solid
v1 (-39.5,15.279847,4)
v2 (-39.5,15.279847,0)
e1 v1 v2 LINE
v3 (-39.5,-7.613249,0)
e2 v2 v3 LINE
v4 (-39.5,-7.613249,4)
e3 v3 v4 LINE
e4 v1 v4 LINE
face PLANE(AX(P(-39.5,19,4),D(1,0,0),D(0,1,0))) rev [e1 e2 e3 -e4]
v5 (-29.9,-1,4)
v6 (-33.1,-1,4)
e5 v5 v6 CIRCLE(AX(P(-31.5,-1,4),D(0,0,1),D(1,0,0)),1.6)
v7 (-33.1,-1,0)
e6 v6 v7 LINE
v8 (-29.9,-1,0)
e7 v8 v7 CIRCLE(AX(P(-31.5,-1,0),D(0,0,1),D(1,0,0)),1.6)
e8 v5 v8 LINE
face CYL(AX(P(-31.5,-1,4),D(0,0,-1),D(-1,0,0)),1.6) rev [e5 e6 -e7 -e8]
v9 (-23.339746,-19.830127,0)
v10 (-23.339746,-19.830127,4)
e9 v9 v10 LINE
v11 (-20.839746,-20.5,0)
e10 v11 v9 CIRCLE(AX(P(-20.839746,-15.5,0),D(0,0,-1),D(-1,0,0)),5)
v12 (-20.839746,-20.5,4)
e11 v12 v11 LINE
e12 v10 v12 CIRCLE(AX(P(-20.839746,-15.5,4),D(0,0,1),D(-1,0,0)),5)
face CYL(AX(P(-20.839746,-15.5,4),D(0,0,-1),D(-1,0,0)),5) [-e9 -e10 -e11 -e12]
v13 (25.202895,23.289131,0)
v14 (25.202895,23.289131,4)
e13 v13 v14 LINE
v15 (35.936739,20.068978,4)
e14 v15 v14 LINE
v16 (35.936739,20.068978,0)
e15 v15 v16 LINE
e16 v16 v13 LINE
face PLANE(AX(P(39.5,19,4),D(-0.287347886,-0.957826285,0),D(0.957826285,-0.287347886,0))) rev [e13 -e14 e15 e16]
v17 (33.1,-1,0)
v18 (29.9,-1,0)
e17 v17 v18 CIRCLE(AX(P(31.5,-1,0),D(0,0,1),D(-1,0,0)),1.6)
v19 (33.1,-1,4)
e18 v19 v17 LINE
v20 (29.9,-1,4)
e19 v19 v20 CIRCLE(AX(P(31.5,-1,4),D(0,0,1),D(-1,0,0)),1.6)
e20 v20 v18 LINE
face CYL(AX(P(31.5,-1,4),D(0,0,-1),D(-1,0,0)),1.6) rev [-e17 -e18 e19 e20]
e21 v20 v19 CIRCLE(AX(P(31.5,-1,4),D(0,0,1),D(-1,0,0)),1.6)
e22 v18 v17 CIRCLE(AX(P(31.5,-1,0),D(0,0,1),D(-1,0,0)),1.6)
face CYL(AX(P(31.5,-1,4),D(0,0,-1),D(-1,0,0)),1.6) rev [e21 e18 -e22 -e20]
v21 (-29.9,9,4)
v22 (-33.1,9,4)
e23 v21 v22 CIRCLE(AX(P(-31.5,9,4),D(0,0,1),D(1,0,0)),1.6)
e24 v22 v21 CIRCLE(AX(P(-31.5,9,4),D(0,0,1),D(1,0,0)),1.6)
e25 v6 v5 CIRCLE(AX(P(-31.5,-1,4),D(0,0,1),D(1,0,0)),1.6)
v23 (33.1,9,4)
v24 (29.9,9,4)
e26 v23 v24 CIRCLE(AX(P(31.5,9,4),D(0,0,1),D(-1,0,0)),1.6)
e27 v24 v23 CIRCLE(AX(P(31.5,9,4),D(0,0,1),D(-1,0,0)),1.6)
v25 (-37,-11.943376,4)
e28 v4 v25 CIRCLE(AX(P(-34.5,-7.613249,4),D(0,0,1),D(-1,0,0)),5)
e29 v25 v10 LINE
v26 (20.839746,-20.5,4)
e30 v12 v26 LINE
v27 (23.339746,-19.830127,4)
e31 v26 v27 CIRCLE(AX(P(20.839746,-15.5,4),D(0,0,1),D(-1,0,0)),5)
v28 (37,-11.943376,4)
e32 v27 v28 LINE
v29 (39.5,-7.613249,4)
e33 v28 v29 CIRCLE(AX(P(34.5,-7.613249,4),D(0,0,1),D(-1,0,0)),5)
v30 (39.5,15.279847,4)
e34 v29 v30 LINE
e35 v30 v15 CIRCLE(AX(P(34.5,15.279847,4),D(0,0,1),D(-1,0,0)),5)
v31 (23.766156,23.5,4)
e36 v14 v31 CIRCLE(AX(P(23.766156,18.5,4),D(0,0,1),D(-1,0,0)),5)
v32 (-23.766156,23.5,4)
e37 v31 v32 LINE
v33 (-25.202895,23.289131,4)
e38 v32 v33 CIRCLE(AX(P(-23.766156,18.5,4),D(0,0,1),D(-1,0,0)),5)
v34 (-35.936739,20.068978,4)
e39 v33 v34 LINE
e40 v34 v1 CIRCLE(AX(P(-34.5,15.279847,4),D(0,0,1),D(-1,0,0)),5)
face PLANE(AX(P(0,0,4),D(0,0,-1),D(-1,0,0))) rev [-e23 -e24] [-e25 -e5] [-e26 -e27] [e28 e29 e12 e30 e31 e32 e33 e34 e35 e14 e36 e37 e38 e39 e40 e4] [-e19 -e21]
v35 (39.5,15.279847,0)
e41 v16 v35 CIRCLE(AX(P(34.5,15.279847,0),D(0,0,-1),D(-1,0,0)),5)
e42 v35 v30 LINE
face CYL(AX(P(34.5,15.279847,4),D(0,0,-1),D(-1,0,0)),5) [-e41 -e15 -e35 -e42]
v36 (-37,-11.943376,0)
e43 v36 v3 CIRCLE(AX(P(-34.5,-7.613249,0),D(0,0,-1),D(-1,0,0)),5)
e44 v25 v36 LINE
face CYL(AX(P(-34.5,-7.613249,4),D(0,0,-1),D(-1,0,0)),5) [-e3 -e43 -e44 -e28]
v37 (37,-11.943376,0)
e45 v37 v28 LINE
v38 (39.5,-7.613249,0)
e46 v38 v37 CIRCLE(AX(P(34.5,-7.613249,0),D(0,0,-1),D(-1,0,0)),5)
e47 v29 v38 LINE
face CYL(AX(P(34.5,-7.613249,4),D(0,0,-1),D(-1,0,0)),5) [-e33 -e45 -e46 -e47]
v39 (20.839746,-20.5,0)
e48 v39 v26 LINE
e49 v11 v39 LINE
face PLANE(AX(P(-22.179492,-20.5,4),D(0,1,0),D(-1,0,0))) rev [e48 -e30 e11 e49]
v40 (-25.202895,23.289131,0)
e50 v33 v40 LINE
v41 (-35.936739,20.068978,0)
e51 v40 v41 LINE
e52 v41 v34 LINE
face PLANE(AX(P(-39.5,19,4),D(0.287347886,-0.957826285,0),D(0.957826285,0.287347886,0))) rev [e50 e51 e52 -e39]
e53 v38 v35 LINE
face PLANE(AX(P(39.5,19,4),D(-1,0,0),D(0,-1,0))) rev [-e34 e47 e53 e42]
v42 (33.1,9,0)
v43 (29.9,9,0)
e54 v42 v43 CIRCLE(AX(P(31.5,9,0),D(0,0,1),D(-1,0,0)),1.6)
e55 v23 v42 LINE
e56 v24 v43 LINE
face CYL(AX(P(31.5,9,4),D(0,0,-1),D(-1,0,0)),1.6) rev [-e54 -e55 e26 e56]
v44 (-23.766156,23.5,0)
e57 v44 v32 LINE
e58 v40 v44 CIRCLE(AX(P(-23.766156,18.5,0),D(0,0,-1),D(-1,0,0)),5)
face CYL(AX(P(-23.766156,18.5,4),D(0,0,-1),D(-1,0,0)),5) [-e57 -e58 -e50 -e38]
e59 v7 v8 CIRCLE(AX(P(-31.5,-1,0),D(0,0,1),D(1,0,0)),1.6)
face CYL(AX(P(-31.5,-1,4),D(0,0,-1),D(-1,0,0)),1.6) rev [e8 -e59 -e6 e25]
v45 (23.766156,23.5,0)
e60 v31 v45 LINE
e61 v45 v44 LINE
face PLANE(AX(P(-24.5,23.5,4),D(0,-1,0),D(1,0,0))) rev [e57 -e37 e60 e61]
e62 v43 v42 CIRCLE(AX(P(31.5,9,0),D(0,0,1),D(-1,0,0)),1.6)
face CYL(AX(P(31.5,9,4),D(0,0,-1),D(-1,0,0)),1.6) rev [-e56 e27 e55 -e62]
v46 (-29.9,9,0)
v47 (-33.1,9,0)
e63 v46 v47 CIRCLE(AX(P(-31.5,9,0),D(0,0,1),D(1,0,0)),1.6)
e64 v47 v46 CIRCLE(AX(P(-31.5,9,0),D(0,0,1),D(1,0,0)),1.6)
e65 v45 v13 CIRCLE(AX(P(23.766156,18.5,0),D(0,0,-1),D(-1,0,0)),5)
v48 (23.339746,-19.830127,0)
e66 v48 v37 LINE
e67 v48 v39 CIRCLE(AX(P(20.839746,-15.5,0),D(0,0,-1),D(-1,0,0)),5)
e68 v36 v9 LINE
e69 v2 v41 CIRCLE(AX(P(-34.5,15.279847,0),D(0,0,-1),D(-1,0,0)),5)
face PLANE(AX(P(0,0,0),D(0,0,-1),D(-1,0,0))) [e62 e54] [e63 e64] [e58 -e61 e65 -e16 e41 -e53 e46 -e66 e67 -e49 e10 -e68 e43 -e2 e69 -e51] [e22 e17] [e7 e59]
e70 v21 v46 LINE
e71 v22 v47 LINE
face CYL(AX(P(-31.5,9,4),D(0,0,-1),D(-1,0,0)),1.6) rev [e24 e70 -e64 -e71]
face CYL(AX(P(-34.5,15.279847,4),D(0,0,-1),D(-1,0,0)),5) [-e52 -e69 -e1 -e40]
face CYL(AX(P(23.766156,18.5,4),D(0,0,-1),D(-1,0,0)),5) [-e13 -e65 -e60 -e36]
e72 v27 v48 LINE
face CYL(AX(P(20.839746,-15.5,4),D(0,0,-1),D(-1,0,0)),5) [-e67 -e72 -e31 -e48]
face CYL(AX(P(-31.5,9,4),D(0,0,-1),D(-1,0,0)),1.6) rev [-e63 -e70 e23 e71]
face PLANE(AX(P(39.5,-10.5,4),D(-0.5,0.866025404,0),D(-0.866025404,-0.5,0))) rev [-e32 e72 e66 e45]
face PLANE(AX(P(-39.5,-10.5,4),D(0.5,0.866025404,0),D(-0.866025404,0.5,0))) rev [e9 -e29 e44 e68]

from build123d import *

# Parameters (mm, degrees)
SKETCH_1_R      = 1.6
EXTRUDE_1_DEPTH = 4
FILLET_R5_1_R   = 5


with BuildPart() as part:
    # 草图1 → 凸台-拉伸1 (new body)
    with BuildSketch(Plane.XY):
        Polygon((-24.5, 23.5), (24.5, 23.5), (39.5, 19), (39.5, -10.5), (22.179491924, -20.5), (-22.179491924, -20.5), (-39.5, -10.5), (-39.5, 19), align=None)
        with Locations((-31.5, 9)):
            Circle(SKETCH_1_R, mode=Mode.SUBTRACT)
        with Locations((-31.5, -1)):
            Circle(SKETCH_1_R, mode=Mode.SUBTRACT)
        with Locations(Location((31.5, -1, 0), (0, 0, 180))):
            Circle(SKETCH_1_R, mode=Mode.SUBTRACT)
        with Locations(Location((31.5, 9, 0), (0, 0, 180))):
            Circle(SKETCH_1_R, mode=Mode.SUBTRACT)
    extrude(amount=EXTRUDE_1_DEPTH)

    # R5 圆角1
    fillet_r5_1_edges = [part.edges().sort_by_distance(p)[0] for p in [
        (-24.5, 23.5, 2),
        (24.5, 23.5, 2),
        (39.5, 19, 2),
        (39.5, -10.5, 2),
        (22.179491924, -20.5, 2),
        (-22.179491924, -20.5, 2),
        (-39.5, -10.5, 2),
        (-39.5, 19, 2),
    ]]
    fillet(fillet_r5_1_edges, radius=FILLET_R5_1_R)


solid = part.part
